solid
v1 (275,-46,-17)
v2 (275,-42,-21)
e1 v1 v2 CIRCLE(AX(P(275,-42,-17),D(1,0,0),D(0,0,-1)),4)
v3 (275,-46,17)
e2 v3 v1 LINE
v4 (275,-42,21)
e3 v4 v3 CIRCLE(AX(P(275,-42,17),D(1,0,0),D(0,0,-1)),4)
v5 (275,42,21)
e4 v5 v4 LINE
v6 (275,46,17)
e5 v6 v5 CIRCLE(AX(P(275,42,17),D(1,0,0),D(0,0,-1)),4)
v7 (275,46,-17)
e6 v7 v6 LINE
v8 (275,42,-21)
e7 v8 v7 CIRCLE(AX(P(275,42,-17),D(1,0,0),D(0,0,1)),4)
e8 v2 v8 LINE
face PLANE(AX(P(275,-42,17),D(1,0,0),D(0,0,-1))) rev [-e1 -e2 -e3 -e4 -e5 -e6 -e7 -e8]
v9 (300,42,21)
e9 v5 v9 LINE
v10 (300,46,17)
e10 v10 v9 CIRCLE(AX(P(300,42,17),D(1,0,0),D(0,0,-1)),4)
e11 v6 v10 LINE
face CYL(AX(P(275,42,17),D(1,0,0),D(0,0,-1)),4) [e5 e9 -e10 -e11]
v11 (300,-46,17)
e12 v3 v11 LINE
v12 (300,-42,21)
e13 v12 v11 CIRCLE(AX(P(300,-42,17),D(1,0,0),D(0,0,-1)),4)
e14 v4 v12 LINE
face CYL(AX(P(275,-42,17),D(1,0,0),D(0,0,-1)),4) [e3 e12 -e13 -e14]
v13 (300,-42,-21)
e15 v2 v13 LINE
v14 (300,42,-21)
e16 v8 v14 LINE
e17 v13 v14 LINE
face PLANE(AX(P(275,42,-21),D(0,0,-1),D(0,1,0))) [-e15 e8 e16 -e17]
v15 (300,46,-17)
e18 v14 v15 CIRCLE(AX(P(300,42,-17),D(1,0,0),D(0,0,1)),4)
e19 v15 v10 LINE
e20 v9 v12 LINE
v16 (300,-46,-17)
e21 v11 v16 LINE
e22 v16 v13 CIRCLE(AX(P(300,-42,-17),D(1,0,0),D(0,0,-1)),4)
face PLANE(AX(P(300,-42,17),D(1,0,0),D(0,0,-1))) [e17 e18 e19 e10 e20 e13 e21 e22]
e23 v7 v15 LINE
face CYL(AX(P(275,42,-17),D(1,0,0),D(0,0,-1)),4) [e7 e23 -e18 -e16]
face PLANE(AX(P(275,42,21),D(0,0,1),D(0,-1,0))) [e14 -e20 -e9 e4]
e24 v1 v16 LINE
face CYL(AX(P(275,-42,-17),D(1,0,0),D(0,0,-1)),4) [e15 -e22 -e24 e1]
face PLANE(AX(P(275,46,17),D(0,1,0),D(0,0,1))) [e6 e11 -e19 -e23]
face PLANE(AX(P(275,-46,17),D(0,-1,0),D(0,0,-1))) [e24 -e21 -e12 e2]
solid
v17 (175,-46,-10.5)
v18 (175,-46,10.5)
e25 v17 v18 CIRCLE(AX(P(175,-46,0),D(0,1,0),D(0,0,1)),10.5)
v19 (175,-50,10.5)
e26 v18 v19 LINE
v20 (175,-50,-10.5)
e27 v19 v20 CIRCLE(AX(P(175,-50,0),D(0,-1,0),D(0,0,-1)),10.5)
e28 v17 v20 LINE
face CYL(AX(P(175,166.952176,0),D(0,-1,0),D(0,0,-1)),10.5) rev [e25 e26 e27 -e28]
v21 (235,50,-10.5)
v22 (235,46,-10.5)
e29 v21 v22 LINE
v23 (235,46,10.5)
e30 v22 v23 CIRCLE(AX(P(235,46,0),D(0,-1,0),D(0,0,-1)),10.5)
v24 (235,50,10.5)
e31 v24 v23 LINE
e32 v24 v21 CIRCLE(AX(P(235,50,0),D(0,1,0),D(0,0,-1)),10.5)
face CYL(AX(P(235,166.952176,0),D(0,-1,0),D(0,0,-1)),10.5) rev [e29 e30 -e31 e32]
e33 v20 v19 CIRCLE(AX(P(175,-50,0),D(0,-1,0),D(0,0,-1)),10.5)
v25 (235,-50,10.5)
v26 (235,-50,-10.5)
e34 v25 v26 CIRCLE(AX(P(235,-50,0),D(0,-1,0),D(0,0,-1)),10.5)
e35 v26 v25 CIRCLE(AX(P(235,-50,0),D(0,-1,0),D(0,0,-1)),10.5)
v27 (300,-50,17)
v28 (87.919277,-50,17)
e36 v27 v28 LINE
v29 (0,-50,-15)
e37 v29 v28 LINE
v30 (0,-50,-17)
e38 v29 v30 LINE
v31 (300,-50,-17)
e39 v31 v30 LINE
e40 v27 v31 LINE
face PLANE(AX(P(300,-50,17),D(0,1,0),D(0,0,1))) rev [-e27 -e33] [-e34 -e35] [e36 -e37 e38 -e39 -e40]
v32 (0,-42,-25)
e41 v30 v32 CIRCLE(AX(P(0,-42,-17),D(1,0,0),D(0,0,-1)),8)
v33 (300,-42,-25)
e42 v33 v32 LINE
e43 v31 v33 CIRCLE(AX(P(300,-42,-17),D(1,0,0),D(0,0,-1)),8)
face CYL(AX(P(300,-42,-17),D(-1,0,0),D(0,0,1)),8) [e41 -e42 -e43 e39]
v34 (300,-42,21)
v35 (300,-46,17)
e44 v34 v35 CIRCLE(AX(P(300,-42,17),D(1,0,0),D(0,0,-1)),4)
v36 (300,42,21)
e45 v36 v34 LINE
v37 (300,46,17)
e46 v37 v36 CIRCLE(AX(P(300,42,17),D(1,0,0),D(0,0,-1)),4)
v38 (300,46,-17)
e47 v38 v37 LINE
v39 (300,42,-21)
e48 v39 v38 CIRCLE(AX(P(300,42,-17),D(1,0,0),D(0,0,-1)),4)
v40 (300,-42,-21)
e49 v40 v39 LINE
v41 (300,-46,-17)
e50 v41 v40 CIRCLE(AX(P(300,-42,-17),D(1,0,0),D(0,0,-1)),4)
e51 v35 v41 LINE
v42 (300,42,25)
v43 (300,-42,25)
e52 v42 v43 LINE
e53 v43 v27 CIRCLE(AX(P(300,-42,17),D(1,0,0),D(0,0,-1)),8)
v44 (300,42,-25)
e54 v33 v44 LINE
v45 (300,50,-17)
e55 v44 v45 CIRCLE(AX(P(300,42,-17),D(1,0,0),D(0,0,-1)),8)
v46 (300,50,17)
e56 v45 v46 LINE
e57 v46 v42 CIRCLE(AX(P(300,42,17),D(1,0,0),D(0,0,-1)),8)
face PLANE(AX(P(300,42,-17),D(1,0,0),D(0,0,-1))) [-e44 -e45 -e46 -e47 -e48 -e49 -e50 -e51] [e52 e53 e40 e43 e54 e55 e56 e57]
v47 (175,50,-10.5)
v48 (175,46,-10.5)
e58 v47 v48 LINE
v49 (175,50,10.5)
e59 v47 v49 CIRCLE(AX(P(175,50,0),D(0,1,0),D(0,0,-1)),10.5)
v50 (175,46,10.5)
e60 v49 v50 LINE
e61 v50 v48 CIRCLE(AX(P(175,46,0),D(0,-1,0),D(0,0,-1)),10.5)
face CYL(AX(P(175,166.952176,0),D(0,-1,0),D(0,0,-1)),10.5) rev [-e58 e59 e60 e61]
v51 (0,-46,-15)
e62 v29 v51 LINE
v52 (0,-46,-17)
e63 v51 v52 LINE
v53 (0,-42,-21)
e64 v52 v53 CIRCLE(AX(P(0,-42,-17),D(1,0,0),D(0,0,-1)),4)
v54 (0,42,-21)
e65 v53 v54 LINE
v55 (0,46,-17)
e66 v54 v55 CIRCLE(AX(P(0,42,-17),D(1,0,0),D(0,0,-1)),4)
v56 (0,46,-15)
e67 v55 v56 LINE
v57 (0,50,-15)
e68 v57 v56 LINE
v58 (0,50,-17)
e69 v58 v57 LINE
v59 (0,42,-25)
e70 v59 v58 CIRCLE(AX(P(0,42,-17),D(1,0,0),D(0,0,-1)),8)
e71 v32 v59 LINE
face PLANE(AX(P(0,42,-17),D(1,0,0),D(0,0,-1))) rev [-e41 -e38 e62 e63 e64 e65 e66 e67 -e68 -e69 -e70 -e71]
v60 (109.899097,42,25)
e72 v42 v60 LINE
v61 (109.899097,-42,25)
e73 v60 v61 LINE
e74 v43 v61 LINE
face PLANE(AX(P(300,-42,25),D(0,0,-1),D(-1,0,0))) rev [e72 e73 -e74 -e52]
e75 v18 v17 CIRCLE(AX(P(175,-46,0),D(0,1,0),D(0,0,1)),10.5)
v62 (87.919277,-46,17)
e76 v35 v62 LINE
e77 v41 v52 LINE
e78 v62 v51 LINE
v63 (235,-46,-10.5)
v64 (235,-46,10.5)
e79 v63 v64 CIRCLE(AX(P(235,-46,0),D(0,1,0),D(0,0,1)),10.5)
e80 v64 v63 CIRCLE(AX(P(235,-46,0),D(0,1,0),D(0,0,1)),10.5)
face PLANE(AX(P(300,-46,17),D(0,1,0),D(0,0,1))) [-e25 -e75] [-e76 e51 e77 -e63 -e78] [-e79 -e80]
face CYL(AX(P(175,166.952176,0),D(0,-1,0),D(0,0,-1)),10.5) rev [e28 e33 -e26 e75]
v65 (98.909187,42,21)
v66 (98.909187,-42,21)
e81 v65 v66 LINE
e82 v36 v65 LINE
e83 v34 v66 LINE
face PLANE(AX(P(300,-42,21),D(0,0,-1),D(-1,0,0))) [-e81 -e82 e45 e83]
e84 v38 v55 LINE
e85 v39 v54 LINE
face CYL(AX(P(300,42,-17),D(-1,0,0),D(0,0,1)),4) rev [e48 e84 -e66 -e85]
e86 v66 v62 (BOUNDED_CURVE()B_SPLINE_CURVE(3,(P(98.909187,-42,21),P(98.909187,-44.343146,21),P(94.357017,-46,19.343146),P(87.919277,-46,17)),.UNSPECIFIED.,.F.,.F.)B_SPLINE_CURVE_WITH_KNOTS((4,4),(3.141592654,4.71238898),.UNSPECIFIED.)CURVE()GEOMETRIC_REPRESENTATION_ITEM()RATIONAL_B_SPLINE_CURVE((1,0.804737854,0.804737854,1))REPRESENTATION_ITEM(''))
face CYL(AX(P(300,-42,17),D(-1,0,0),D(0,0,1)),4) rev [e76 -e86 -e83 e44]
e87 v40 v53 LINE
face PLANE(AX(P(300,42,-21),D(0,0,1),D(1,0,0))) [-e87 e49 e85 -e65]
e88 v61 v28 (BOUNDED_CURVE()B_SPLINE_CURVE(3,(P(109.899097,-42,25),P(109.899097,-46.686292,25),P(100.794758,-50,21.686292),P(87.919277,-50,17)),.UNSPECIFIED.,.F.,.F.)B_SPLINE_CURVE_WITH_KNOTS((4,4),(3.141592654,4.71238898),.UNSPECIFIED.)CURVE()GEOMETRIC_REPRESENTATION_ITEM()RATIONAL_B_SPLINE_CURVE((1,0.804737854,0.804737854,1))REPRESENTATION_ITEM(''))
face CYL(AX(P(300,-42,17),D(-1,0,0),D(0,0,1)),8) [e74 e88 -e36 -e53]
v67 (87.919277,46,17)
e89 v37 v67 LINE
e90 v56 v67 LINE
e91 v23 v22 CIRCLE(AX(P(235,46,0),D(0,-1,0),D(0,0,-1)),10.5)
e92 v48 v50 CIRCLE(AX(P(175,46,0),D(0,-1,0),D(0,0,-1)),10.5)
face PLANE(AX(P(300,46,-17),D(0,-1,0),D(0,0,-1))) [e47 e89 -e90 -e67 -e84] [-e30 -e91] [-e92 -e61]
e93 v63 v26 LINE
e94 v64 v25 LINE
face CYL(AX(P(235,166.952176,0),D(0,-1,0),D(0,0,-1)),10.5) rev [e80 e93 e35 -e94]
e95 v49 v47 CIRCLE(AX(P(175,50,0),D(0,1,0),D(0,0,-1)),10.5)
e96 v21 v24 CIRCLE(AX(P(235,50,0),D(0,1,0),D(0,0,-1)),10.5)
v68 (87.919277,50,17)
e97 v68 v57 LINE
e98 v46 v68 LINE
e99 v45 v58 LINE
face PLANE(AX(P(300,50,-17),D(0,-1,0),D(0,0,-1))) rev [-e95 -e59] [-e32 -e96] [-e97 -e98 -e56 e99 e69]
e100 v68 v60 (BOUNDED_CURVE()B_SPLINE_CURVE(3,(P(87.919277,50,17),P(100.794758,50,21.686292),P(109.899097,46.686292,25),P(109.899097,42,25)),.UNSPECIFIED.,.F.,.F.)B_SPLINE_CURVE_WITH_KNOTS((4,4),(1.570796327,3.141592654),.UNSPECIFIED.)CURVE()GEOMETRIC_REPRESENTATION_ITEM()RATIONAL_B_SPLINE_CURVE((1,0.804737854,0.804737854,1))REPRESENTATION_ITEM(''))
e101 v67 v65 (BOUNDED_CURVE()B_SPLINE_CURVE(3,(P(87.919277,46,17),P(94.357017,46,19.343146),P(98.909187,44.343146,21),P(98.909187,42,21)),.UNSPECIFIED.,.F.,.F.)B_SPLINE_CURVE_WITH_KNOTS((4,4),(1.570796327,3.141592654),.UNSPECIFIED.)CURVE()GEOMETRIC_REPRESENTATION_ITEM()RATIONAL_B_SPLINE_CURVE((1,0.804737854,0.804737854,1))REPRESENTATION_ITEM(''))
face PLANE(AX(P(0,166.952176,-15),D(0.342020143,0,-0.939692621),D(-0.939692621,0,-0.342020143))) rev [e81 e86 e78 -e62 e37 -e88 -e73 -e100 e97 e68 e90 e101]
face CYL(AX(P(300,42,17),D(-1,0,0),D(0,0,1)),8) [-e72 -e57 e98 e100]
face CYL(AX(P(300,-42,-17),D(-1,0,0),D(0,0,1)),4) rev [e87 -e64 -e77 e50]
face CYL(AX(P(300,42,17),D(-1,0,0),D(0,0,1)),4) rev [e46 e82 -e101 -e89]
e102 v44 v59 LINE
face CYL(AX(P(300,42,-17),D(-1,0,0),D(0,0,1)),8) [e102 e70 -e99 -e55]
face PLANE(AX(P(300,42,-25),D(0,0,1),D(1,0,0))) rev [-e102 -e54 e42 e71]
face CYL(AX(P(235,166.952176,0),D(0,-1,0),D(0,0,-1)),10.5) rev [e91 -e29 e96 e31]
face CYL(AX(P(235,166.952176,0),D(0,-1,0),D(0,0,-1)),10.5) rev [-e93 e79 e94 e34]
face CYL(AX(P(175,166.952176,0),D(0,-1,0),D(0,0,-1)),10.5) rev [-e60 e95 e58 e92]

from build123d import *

# Parameters (mm, degrees)
F_100_X_50_X_4_1_DEPTH = 300
CUT_EXTRUDE_1_REACH    = 319.214
SKETCH_2_R             = 10.5
EXTRUDE_1_DEPTH        = 25


with BuildPart() as part:
    # Sketch1 → 矩形管 100 X 50 X 4(1) (new body)
    with BuildSketch(Plane(origin=(0, 0, 0), x_dir=(0, 0, -1), z_dir=(1, 0, 0))):
        with BuildLine():
            Line((-17, -50), (17, -50))
            ThreePointArc((17, -50), (22.656854249, -47.656854249), (25, -42))
            Line((25, -42), (25, 42))
            ThreePointArc((25, 42), (22.656854249, 47.656854249), (17, 50))
            Line((17, 50), (-17, 50))
            ThreePointArc((-17, 50), (-22.656854249, 47.656854249), (-25, 42))
            Line((-25, 42), (-25, -42))
            ThreePointArc((-25, -42), (-22.656854249, -47.656854249), (-17, -50))
        make_face()
        with BuildLine():
            Line((-17, -46), (17, -46))
            ThreePointArc((17, -46), (19.828427125, -44.828427125), (21, -42))
            Line((21, -42), (21, 42))
            ThreePointArc((21, 42), (19.828427125, 44.828427125), (17, 46))
            Line((17, 46), (-17, 46))
            ThreePointArc((-17, 46), (-19.828427125, 44.828427125), (-21, 42))
            Line((-21, 42), (-21, -42))
            ThreePointArc((-21, -42), (-19.828427125, -44.828427125), (-17, -46))
        make_face(mode=Mode.SUBTRACT)
    extrude(amount=F_100_X_50_X_4_1_DEPTH)

    # 切除-拉伸1: up to this face of the body (flat: up to its plane)
    cut_extrude_1_end = Plane(part.part.faces().sort_by_distance((150, 50, 0))[0])
    # 草图2 → 切除-拉伸1 (cut, up to the picked face)
    with BuildSketch(Plane.XZ.offset(50), mode=Mode.PRIVATE) as cut_extrude_1_sk1:
        with Locations(Location((235, 0, 0), (0, 0, 270))):
            Circle(SKETCH_2_R)
    cut_extrude_1_tool1 = split(extrude(cut_extrude_1_sk1.sketch, amount=-CUT_EXTRUDE_1_REACH, mode=Mode.PRIVATE), bisect_by=cut_extrude_1_end, keep=Keep.BOTH, mode=Mode.PRIVATE)
    # 草图2 → 切除-拉伸1 (cut, up to the picked face)
    with BuildSketch(Plane.XZ.offset(50), mode=Mode.PRIVATE) as cut_extrude_1_sk2:
        with Locations(Location((175, 0, 0), (0, 0, 270))):
            Circle(SKETCH_2_R)
    cut_extrude_1_tool2 = split(extrude(cut_extrude_1_sk2.sketch, amount=-CUT_EXTRUDE_1_REACH, mode=Mode.PRIVATE), bisect_by=cut_extrude_1_end, keep=Keep.BOTH, mode=Mode.PRIVATE)
    # 草图2 → 切除-拉伸1 (cut, up to the picked face)
    with BuildSketch(Plane.XZ.offset(50), mode=Mode.PRIVATE) as cut_extrude_1_sk3:
        Polygon((0, -15), (109.899096778, 25), (0, 25), align=None)
    cut_extrude_1_tool3 = split(extrude(cut_extrude_1_sk3.sketch, amount=-CUT_EXTRUDE_1_REACH, mode=Mode.PRIVATE), bisect_by=cut_extrude_1_end, keep=Keep.BOTH, mode=Mode.PRIVATE)
    add(cut_extrude_1_tool1.solids().sort_by(Axis((235, -50, 0), (0, 1, 0)))[0], mode=Mode.SUBTRACT)
    add(cut_extrude_1_tool2.solids().sort_by(Axis((175, -50, 0), (0, 1, 0)))[0], mode=Mode.SUBTRACT)
    add(cut_extrude_1_tool3.solids().sort_by(Axis((36.633032, -50, 11.666667), (0, 1, 0)))[0], mode=Mode.SUBTRACT)


with BuildPart() as body_2:
    # 草图3 → 凸台-拉伸1 (new body)
    with BuildSketch(Plane(origin=(300, 0, 0), x_dir=(0, 0, -1), z_dir=(1, 0, 0))):
        with BuildLine():
            Line((-17, 46), (17, 46))
            ThreePointArc((17, 46), (19.828427125, 44.828427125), (21, 42))
            Line((21, 42), (21, -42))
            ThreePointArc((21, -42), (19.828427125, -44.828427125), (17, -46))
            Line((17, -46), (-17, -46))
            ThreePointArc((-17, -46), (-19.828427125, -44.828427125), (-21, -42))
            Line((-21, -42), (-21, 42))
            ThreePointArc((-21, 42), (-19.828427125, 44.828427125), (-17, 46))
        make_face()
    extrude(amount=-EXTRUDE_1_DEPTH)


solid = Compound([part.part, body_2.part])
